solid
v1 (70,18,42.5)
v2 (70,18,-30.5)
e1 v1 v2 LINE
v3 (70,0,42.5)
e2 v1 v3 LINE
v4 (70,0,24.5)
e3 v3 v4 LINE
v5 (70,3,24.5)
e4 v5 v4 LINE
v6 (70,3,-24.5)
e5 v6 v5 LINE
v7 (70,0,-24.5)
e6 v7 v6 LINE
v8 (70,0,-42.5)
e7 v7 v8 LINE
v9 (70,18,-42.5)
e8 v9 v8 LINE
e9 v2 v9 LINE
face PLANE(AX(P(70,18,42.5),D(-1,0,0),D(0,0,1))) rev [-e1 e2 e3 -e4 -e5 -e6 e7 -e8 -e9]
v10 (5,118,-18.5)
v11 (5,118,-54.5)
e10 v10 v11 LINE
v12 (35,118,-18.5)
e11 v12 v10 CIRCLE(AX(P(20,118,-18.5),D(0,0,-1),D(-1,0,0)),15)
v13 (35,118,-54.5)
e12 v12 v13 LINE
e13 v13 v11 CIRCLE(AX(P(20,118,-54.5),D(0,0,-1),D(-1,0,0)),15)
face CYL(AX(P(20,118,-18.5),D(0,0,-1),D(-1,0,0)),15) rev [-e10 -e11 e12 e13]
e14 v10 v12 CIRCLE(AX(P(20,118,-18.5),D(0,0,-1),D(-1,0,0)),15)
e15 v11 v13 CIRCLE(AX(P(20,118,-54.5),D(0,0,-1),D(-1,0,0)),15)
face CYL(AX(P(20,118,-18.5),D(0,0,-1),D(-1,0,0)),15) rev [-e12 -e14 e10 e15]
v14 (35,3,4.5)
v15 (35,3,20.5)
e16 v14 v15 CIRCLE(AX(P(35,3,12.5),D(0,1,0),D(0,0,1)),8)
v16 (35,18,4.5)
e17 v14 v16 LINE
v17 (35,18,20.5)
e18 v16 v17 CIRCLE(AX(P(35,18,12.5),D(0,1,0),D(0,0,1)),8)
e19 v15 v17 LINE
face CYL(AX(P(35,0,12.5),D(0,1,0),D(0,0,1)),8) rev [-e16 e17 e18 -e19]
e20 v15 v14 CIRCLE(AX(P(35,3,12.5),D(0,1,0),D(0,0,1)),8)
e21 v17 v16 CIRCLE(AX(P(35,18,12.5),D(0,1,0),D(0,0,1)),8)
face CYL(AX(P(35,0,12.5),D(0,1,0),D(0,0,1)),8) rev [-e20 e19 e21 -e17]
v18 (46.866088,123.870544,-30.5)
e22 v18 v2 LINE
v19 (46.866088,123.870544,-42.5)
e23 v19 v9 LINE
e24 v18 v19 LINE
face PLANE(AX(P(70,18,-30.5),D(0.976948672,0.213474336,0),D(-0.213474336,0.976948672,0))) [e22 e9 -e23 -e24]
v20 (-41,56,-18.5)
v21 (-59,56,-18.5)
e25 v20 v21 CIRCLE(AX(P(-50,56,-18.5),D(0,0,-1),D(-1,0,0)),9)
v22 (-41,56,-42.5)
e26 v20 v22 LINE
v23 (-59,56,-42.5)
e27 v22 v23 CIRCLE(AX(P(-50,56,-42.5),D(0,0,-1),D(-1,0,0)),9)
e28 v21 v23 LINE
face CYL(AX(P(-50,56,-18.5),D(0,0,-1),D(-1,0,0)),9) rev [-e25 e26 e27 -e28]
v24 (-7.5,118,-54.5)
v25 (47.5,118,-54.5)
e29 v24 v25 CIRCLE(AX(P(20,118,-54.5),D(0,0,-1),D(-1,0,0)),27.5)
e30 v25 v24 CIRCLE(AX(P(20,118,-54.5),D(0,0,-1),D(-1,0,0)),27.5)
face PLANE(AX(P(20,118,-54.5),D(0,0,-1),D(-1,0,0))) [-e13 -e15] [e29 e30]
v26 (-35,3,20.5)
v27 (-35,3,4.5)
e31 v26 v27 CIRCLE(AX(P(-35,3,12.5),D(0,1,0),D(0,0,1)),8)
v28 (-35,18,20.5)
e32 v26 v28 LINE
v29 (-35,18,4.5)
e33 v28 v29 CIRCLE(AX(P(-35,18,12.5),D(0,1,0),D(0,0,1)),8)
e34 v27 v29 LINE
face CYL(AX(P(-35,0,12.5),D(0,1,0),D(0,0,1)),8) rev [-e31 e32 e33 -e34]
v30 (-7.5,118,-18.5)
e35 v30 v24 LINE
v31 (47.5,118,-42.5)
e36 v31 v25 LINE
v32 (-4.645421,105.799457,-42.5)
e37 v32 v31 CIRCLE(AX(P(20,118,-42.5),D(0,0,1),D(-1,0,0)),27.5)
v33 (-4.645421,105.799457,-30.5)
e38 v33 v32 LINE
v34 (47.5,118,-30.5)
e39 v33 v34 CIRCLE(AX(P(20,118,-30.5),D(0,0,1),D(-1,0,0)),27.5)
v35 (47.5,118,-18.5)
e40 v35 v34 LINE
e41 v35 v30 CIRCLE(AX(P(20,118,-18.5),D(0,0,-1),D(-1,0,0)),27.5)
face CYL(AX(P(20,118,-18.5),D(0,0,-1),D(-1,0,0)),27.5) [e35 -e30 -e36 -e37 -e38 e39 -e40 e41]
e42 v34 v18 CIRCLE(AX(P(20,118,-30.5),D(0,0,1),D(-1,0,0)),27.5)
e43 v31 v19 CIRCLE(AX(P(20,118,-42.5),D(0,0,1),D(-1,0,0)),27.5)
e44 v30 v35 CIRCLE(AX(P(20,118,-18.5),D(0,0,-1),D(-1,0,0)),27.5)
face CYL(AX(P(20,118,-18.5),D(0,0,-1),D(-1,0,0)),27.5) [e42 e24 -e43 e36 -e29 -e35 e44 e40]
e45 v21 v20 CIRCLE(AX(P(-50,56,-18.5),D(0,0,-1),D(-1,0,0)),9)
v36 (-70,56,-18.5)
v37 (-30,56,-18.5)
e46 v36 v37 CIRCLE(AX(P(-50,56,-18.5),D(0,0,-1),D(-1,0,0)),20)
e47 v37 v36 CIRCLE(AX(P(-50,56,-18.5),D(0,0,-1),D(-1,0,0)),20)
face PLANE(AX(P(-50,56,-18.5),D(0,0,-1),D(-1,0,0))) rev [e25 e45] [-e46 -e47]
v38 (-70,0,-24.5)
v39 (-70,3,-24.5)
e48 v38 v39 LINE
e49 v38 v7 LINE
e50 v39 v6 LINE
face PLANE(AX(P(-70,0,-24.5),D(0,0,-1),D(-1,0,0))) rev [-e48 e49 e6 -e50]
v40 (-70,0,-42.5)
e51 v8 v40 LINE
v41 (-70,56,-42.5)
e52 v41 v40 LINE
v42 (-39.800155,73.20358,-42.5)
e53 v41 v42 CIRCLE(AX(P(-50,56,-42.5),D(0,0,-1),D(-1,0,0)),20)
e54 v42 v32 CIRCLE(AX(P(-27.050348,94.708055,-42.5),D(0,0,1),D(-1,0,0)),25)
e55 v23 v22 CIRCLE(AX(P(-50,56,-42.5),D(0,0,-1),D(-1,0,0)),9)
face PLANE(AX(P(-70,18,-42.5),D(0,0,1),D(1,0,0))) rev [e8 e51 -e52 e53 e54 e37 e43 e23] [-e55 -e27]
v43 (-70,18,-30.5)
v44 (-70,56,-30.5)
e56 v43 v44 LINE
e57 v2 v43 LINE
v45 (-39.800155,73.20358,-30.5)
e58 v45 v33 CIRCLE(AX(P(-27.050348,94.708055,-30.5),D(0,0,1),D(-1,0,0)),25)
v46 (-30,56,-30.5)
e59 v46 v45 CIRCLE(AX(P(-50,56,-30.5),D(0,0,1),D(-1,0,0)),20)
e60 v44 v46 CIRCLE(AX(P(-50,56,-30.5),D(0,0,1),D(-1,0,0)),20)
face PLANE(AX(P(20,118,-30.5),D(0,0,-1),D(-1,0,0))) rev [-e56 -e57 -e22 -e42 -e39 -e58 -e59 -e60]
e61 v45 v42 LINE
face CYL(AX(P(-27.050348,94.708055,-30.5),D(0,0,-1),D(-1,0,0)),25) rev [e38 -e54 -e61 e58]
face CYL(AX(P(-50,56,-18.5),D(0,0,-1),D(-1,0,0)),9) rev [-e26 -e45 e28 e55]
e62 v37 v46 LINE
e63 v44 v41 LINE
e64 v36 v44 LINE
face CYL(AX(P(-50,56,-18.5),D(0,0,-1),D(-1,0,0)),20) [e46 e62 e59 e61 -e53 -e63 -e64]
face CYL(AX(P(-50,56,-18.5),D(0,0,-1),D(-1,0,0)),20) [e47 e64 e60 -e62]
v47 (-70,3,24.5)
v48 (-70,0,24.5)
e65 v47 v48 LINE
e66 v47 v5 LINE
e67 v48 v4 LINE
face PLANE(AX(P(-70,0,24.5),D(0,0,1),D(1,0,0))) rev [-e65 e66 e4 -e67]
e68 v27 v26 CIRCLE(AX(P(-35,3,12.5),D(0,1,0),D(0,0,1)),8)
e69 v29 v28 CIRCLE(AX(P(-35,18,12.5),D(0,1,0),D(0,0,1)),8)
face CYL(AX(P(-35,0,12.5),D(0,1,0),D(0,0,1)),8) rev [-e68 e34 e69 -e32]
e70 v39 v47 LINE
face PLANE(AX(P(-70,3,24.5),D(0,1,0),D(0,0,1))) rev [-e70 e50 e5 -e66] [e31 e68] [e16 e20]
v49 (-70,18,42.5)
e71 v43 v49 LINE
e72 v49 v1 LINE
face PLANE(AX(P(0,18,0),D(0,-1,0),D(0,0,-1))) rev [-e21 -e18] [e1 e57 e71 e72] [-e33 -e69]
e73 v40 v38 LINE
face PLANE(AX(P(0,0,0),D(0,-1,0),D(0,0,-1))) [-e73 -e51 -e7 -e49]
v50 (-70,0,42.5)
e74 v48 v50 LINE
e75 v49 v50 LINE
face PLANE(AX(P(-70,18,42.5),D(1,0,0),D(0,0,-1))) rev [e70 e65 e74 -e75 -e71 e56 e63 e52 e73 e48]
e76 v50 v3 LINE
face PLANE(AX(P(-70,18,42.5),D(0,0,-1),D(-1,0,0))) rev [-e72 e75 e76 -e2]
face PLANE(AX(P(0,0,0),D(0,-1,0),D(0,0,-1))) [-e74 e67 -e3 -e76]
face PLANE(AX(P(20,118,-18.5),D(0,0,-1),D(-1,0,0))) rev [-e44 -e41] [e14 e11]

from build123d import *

# Parameters (mm, degrees)
BASE_PLATE_SKETCH_W          = 140
BASE_PLATE_SKETCH_H          = 85
BASE_PLATE_DEPTH             = 18
UNDERSIDE_GROOVE_SKETCH_W    = 49
UNDERSIDE_GROOVE_SKETCH_H    = 3
UNDERSIDE_GROOVE_DEPTH       = 148.411838059
BASE_HOLES_SKETCH_R          = 8
BASE_HOLES_DEPTH             = 84.846586096
UPRIGHT_LUG_PLATE_DEPTH      = 12
UPRIGHT_LUG_PLATE_DEPTH_BACK = 24
UPRIGHT_LUG_PLATE_SKETCH_R   = 27.5
UPRIGHT_LUG_PLATE_SKETCH_R_2 = 15
SIDE_GUSSET_SKETCH_R         = 20
SIDE_GUSSET_SKETCH_R_2       = 9
SIDE_GUSSET_DEPTH            = 24
HINGE_BOSS_EXTENSION_DEPTH   = 12


with BuildPart() as part:
    # Base Plate Sketch → Base Plate (new body)
    with BuildSketch(Plane(origin=(0, 0, 0), x_dir=(1, 0, 0), z_dir=(0, 1, 0))):
        Rectangle(BASE_PLATE_SKETCH_W, BASE_PLATE_SKETCH_H)
    extrude(amount=BASE_PLATE_DEPTH)

    # Underside Groove Sketch → Underside Groove (cut, through all)
    with BuildSketch(Plane(origin=(70, 0, 0), x_dir=(0, 0, -1), z_dir=(1, 0, 0))):
        with Locations((0, 1.5)):
            Rectangle(UNDERSIDE_GROOVE_SKETCH_W, UNDERSIDE_GROOVE_SKETCH_H)
    extrude(amount=-UNDERSIDE_GROOVE_DEPTH, mode=Mode.SUBTRACT)

    # Base Holes Sketch → Base Holes (cut, through all)
    with BuildSketch(Plane(origin=(0, 18, 0), x_dir=(1, 0, 0), z_dir=(0, 1, 0))):
        with Locations(Location((-35, -12.5, 0), (0, 0, 270))):
            Circle(BASE_HOLES_SKETCH_R)
        with Locations(Location((35, -12.5, 0), (0, 0, 270))):
            Circle(BASE_HOLES_SKETCH_R)
    extrude(amount=-BASE_HOLES_DEPTH, mode=Mode.SUBTRACT)



with BuildPart() as body_2:
    # Upright Lug Plate Sketch → Upright Lug Plate (new, two sides: drawn at the far end of the back side and taken through both)
    with BuildSketch(Plane(origin=(0, 0, -42.5), x_dir=(-1, 0, 0), z_dir=(0, 0, -1)).offset(-UPRIGHT_LUG_PLATE_DEPTH_BACK)):
        with Locations((-20, 118)):
            Circle(UPRIGHT_LUG_PLATE_SKETCH_R)
        with Locations((-20, 118)):
            Circle(UPRIGHT_LUG_PLATE_SKETCH_R_2, mode=Mode.SUBTRACT)
    extrude(amount=UPRIGHT_LUG_PLATE_DEPTH + UPRIGHT_LUG_PLATE_DEPTH_BACK)


with BuildPart() as body_3:
    # Side Gusset Sketch → Side Gusset (new body)
    with BuildSketch(Plane(origin=(0, 0, -42.5), x_dir=(-1, 0, 0), z_dir=(0, 0, -1))):
        with Locations((50, 56)):
            Circle(SIDE_GUSSET_SKETCH_R)
        with Locations((50, 56)):
            Circle(SIDE_GUSSET_SKETCH_R_2, mode=Mode.SUBTRACT)
    extrude(amount=-SIDE_GUSSET_DEPTH)


with BuildPart() as part_1:
    add(part.part)

    add(body_2.part)  # Hinge Boss Extension merges body 2

    add(body_3.part)  # Hinge Boss Extension merges body 3
    # Hinge Boss Extension Sketch → Hinge Boss Extension (add)
    with BuildSketch(Plane(origin=(0, 0, -42.5), x_dir=(-1, 0, 0), z_dir=(0, 0, -1))):
        with BuildLine():
            Line((70, 18), (70, 56))
            ThreePointArc((70, 56), (40.100426872, 38.621897345), (39.800154813, 73.203579806))
            ThreePointArc((39.800154813, 73.203579806), (10.05246179, 76.375791932), (4.645420553, 105.799457153))
            ThreePointArc((4.645420553, 105.799457153), (-29.103509689, 92.050508457), (-46.866088482, 123.870544241))
            Line((-46.866088482, 123.870544241), (-70, 18))
            Line((-70, 18), (70, 18))
        make_face()
    extrude(amount=-HINGE_BOSS_EXTENSION_DEPTH)


solid = part_1.part
